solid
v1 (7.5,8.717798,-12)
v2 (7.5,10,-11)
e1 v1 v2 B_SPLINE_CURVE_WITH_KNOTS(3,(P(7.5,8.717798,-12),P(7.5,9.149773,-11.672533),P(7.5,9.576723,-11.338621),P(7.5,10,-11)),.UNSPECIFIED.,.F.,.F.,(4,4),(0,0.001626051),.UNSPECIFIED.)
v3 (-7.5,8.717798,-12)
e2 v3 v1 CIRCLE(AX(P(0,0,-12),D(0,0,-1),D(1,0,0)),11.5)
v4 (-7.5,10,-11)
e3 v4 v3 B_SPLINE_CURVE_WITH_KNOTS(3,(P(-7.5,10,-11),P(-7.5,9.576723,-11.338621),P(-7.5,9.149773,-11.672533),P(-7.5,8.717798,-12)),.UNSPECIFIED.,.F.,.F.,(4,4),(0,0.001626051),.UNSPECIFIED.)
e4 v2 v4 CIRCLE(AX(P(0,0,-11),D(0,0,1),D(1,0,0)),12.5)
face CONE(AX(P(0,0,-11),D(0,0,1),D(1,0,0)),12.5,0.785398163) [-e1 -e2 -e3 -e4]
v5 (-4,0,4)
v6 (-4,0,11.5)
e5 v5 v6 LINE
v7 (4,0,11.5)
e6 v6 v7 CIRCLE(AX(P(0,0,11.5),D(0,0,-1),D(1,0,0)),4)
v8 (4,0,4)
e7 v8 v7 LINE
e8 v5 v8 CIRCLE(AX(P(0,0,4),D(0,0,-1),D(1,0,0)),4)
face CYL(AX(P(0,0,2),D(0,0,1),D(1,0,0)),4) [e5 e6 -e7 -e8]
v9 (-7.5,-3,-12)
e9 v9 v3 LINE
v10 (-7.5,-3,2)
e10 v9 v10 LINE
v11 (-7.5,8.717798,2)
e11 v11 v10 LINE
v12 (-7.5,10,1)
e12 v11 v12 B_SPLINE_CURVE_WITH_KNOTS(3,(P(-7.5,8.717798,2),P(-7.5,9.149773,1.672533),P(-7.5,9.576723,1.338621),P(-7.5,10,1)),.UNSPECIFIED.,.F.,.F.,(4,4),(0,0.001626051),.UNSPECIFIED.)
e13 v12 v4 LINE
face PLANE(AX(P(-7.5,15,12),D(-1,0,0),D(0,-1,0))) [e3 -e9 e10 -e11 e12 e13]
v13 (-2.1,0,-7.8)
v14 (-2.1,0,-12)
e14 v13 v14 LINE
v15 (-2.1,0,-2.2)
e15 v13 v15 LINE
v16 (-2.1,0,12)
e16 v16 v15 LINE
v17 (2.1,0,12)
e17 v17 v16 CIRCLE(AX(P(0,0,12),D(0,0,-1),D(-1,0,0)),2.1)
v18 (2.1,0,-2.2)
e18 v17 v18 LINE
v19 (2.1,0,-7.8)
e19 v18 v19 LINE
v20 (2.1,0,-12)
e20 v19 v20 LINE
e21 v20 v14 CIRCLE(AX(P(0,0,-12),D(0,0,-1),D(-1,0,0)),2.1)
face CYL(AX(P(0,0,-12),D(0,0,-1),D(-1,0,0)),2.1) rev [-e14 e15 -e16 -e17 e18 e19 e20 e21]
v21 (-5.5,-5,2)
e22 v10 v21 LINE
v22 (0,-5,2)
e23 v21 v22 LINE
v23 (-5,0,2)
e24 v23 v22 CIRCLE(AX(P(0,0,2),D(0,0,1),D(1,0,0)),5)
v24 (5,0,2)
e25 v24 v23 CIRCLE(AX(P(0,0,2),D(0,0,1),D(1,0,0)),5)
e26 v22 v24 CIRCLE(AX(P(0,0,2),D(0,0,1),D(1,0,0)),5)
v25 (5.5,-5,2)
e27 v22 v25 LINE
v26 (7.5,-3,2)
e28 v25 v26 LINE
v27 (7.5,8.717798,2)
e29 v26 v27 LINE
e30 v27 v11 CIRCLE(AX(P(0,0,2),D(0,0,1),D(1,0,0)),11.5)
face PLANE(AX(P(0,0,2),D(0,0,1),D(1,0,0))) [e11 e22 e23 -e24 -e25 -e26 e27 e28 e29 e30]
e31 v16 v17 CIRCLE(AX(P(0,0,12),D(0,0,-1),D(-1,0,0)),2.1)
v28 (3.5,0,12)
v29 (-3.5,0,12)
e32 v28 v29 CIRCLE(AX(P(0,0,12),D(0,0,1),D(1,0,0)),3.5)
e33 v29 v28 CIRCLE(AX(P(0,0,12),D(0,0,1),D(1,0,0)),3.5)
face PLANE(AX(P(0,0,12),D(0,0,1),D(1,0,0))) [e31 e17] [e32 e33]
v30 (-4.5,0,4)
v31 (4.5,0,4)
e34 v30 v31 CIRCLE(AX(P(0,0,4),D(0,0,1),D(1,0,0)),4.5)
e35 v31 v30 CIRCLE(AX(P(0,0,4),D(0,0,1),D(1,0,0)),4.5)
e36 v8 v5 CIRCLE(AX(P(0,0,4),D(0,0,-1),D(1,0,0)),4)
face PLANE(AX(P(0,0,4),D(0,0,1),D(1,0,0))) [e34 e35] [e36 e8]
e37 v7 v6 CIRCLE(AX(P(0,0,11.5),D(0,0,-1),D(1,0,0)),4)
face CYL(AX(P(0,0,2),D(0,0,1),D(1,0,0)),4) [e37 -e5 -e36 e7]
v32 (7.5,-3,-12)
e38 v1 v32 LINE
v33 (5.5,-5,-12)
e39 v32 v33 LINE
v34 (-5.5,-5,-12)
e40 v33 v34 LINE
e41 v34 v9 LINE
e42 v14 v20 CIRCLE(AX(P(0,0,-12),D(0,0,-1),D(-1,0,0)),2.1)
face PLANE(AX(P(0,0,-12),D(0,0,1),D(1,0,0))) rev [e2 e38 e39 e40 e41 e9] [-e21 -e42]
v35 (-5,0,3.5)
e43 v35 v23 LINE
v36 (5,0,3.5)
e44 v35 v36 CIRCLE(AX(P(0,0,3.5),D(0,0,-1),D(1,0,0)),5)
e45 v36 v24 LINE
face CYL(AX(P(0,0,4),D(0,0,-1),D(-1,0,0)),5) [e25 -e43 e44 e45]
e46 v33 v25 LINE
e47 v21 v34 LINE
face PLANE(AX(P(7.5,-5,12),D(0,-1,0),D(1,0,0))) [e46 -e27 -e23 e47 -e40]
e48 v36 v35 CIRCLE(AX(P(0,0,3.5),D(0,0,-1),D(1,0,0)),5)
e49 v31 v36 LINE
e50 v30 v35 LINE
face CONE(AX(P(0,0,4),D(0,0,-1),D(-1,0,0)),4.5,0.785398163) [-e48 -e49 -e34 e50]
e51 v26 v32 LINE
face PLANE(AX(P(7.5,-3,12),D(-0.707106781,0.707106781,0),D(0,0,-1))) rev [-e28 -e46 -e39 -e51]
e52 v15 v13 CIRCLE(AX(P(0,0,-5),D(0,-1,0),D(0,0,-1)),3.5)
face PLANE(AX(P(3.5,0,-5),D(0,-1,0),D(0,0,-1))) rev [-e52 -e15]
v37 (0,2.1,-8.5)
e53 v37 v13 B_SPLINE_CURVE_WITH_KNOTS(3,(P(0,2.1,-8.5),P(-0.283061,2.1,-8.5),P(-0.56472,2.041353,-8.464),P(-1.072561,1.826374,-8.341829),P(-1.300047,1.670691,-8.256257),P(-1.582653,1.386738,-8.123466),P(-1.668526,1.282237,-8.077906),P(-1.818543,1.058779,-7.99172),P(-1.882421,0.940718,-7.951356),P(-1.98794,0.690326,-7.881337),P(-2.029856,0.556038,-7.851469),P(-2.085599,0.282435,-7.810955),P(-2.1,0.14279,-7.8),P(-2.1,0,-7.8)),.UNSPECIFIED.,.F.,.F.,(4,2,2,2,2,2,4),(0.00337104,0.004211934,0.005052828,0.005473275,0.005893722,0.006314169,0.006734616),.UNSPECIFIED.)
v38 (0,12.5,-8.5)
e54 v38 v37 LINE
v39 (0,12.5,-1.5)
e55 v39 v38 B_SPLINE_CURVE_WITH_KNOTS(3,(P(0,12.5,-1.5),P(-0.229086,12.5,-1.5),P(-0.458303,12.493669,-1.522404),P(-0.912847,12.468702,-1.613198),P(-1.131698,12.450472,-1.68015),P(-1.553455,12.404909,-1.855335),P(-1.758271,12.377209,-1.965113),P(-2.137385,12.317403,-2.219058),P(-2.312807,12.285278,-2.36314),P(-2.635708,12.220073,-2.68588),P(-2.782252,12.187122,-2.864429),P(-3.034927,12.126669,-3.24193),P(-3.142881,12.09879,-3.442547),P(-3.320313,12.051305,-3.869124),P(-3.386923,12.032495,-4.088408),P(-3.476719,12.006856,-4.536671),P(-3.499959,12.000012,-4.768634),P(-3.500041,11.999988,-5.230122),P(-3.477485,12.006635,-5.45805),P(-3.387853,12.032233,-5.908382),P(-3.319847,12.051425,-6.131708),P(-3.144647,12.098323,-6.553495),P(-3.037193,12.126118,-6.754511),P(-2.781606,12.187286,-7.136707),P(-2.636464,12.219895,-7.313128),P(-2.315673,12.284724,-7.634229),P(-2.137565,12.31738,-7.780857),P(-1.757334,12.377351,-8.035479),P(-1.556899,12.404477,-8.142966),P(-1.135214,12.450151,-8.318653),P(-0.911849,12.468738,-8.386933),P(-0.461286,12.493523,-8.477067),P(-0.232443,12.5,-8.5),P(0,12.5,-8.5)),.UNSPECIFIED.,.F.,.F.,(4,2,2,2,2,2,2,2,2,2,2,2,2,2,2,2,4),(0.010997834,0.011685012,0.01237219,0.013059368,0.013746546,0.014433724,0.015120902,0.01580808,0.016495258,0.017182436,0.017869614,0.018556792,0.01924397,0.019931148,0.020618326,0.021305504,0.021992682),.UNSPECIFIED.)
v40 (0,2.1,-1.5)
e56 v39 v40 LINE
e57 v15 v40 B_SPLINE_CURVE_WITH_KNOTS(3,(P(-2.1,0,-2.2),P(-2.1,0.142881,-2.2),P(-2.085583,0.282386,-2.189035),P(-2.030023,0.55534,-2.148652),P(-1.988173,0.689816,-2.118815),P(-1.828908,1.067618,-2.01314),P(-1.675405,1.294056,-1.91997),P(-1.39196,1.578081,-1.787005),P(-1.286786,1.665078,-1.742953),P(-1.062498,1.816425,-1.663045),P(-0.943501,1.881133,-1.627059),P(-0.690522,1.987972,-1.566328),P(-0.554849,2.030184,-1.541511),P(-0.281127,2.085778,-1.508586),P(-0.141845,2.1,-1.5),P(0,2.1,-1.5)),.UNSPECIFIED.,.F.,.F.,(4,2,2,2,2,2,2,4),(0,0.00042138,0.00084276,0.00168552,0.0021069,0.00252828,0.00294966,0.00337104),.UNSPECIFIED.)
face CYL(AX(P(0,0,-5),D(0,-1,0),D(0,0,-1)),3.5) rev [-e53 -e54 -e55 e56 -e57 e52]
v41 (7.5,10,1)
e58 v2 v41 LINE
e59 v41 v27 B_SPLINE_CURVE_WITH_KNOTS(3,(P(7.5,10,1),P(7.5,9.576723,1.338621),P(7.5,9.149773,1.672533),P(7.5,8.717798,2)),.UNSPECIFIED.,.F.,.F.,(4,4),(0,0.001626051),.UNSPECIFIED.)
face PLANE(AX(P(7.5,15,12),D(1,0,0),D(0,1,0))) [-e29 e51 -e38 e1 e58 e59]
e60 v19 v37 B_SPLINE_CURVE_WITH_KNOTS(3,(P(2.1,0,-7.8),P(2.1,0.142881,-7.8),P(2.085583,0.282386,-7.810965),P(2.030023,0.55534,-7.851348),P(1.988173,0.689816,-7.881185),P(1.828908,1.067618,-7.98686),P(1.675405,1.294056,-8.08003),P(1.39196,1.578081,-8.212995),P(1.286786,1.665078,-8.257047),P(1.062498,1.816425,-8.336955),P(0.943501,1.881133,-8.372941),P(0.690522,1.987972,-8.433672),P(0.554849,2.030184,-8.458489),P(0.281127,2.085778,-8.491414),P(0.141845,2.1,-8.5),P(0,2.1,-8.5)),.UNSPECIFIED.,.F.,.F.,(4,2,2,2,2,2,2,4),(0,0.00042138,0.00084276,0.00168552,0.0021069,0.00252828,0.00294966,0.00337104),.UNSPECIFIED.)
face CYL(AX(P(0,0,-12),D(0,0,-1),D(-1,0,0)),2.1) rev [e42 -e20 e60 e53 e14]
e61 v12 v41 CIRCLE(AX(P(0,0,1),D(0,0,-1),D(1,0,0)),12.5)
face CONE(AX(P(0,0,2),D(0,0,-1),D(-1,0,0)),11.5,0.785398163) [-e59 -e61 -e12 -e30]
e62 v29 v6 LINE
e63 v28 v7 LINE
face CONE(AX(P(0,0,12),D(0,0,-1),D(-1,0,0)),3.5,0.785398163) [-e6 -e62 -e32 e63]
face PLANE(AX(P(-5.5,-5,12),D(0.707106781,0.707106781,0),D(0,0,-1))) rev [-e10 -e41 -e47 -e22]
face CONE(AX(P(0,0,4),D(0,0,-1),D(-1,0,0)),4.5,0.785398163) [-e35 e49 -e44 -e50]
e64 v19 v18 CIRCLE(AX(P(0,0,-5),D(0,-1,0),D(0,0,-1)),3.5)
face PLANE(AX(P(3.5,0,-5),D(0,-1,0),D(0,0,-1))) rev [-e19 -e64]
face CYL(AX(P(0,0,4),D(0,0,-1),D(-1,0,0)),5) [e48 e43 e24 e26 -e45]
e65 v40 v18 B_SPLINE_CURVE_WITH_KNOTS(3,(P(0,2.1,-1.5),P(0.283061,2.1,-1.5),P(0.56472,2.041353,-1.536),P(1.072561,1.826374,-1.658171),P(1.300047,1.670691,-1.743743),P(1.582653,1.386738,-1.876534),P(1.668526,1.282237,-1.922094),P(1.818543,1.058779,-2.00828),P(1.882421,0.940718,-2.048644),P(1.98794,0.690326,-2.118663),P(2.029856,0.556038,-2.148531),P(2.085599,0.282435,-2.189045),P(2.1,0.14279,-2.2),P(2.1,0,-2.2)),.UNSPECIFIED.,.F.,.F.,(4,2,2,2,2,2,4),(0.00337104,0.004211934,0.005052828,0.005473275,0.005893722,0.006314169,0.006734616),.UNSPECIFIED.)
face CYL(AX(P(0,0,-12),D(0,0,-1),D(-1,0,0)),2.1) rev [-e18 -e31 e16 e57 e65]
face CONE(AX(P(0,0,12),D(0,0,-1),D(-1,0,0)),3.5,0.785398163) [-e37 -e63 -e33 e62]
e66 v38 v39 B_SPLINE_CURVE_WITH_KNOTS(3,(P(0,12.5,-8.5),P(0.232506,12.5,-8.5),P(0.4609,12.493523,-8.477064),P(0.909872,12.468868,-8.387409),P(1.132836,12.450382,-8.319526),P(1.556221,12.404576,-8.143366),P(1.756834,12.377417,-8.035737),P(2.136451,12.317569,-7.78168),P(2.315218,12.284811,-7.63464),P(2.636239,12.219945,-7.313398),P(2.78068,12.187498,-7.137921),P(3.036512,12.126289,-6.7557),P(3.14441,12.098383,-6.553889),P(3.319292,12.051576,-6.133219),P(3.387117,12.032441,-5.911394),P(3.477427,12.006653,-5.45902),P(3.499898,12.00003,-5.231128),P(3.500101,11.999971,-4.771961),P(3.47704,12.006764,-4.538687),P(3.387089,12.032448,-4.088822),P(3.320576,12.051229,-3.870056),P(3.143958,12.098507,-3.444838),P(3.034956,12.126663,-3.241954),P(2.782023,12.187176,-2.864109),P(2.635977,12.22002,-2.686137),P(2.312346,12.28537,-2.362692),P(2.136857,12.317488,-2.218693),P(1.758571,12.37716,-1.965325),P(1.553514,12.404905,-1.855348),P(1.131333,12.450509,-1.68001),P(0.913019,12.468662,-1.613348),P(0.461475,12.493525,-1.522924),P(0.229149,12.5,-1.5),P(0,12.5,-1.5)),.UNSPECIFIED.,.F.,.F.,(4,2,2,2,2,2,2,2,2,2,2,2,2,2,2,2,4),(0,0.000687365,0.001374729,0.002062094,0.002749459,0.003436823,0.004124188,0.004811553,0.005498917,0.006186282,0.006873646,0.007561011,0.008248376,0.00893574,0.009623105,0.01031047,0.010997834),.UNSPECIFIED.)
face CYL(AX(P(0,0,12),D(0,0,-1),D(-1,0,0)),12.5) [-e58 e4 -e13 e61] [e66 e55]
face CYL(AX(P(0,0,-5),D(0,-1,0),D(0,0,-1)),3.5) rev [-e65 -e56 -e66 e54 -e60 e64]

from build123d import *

# Parameters (mm, degrees)
SKETCH1_R           = 12.5
BOSS_EXTRUDE1_DEPTH = 12
SKETCH2_OUTSIDE_W   = 35.546
SKETCH2_OUTSIDE_H   = 35.546
SKETCH2_OUTSIDE_R   = 4
CUT_EXTRUDE1_DEPTH  = 10
SKETCH9_OUTSIDE_W   = 35.546
SKETCH9_OUTSIDE_H   = 35.546
SKETCH9_OUTSIDE_W_2 = 15
SKETCH9_OUTSIDE_H_2 = 20
CUT_EXTRUDE2_DEPTH  = 30.807717122
M5_TAPPED_HOLE1_D   = 4.2
BOSS_EXTRUDE2_START = 2
SKETCH8_R           = 5
SKETCH8_R_2         = 4
BOSS_EXTRUDE2_DEPTH = 2
SKETCH6_W           = 3.5
SKETCH6_H           = 12.5
CHAMFER1_SIZE       = 0.5
CHAMFER2_SIZE       = 2
CHAMFER3_SIZE       = 1


with BuildPart() as part:
    # Sketch1 → Boss-Extrude1 (new, symmetric)
    with BuildSketch(Plane.XY):
        Circle(SKETCH1_R)
    extrude(amount=BOSS_EXTRUDE1_DEPTH, both=True)

    # Sketch2 outside → Cut-Extrude1 (cut)
    with BuildSketch(Plane.XY.offset(12)):
        Rectangle(SKETCH2_OUTSIDE_W, SKETCH2_OUTSIDE_H)
        Circle(SKETCH2_OUTSIDE_R, mode=Mode.SUBTRACT)
    extrude(amount=-CUT_EXTRUDE1_DEPTH, mode=Mode.SUBTRACT)

    # Sketch9 outside → Cut-Extrude2 (cut, through all)
    with BuildSketch(Plane(origin=(0, 0, -12), x_dir=(-1, 0, 0), z_dir=(0, 0, -1))):
        Rectangle(SKETCH9_OUTSIDE_W, SKETCH9_OUTSIDE_H)
        with Locations((0, 5)):
            Rectangle(SKETCH9_OUTSIDE_W_2, SKETCH9_OUTSIDE_H_2, mode=Mode.SUBTRACT)
    extrude(amount=-CUT_EXTRUDE2_DEPTH, mode=Mode.SUBTRACT)

    # M5 Tapped Hole1 (through all)
    with Locations(Plane(origin=(0, 0, -12), x_dir=(-1, 0, 0), z_dir=(0, 0, -1))):
        with Locations((0, 0)):
            Hole(M5_TAPPED_HOLE1_D / 2)

    # Sketch8 → Boss-Extrude2 (add)
    with BuildSketch(Plane.XY.offset(2).offset(BOSS_EXTRUDE2_START)):
        with Locations(Location((0, 0, 0), (0, 0, 270))):
            Circle(SKETCH8_R)
        Circle(SKETCH8_R_2, mode=Mode.SUBTRACT)
    extrude(amount=-BOSS_EXTRUDE2_DEPTH)

    # Sketch6 → M8x1.0 Tapped Hole1 (revolve, cut)
    with BuildSketch(Plane(origin=(0, 0, -5), x_dir=(0, 0, -1), z_dir=(1, 0, 0))):
        with Locations((1.75, 6.25)):
            Rectangle(SKETCH6_W, SKETCH6_H)
    revolve(axis=Axis((0, -6.35, -5), (0, 1, 0)), mode=Mode.SUBTRACT)

    # Chamfer1
    chamfer1_edges = [part.edges().sort_by_distance(p)[0] for p in [
        (-4, 0, 12),
        (0, 5, 4),
    ]]
    chamfer(chamfer1_edges, length=CHAMFER1_SIZE)

    # Chamfer2
    chamfer2_edges = [part.edges().sort_by_distance(p)[0] for p in [
        (-7.5, -5, -5),
        (7.5, -5, -5),
    ]]
    chamfer(chamfer2_edges, length=CHAMFER2_SIZE)

    # Chamfer3
    chamfer3_edges = [part.edges().sort_by_distance(p)[0] for p in [
        (0, 12.5, -12),
        (0, 12.5, 2),
    ]]
    chamfer(chamfer3_edges, length=CHAMFER3_SIZE)


solid = part.part
